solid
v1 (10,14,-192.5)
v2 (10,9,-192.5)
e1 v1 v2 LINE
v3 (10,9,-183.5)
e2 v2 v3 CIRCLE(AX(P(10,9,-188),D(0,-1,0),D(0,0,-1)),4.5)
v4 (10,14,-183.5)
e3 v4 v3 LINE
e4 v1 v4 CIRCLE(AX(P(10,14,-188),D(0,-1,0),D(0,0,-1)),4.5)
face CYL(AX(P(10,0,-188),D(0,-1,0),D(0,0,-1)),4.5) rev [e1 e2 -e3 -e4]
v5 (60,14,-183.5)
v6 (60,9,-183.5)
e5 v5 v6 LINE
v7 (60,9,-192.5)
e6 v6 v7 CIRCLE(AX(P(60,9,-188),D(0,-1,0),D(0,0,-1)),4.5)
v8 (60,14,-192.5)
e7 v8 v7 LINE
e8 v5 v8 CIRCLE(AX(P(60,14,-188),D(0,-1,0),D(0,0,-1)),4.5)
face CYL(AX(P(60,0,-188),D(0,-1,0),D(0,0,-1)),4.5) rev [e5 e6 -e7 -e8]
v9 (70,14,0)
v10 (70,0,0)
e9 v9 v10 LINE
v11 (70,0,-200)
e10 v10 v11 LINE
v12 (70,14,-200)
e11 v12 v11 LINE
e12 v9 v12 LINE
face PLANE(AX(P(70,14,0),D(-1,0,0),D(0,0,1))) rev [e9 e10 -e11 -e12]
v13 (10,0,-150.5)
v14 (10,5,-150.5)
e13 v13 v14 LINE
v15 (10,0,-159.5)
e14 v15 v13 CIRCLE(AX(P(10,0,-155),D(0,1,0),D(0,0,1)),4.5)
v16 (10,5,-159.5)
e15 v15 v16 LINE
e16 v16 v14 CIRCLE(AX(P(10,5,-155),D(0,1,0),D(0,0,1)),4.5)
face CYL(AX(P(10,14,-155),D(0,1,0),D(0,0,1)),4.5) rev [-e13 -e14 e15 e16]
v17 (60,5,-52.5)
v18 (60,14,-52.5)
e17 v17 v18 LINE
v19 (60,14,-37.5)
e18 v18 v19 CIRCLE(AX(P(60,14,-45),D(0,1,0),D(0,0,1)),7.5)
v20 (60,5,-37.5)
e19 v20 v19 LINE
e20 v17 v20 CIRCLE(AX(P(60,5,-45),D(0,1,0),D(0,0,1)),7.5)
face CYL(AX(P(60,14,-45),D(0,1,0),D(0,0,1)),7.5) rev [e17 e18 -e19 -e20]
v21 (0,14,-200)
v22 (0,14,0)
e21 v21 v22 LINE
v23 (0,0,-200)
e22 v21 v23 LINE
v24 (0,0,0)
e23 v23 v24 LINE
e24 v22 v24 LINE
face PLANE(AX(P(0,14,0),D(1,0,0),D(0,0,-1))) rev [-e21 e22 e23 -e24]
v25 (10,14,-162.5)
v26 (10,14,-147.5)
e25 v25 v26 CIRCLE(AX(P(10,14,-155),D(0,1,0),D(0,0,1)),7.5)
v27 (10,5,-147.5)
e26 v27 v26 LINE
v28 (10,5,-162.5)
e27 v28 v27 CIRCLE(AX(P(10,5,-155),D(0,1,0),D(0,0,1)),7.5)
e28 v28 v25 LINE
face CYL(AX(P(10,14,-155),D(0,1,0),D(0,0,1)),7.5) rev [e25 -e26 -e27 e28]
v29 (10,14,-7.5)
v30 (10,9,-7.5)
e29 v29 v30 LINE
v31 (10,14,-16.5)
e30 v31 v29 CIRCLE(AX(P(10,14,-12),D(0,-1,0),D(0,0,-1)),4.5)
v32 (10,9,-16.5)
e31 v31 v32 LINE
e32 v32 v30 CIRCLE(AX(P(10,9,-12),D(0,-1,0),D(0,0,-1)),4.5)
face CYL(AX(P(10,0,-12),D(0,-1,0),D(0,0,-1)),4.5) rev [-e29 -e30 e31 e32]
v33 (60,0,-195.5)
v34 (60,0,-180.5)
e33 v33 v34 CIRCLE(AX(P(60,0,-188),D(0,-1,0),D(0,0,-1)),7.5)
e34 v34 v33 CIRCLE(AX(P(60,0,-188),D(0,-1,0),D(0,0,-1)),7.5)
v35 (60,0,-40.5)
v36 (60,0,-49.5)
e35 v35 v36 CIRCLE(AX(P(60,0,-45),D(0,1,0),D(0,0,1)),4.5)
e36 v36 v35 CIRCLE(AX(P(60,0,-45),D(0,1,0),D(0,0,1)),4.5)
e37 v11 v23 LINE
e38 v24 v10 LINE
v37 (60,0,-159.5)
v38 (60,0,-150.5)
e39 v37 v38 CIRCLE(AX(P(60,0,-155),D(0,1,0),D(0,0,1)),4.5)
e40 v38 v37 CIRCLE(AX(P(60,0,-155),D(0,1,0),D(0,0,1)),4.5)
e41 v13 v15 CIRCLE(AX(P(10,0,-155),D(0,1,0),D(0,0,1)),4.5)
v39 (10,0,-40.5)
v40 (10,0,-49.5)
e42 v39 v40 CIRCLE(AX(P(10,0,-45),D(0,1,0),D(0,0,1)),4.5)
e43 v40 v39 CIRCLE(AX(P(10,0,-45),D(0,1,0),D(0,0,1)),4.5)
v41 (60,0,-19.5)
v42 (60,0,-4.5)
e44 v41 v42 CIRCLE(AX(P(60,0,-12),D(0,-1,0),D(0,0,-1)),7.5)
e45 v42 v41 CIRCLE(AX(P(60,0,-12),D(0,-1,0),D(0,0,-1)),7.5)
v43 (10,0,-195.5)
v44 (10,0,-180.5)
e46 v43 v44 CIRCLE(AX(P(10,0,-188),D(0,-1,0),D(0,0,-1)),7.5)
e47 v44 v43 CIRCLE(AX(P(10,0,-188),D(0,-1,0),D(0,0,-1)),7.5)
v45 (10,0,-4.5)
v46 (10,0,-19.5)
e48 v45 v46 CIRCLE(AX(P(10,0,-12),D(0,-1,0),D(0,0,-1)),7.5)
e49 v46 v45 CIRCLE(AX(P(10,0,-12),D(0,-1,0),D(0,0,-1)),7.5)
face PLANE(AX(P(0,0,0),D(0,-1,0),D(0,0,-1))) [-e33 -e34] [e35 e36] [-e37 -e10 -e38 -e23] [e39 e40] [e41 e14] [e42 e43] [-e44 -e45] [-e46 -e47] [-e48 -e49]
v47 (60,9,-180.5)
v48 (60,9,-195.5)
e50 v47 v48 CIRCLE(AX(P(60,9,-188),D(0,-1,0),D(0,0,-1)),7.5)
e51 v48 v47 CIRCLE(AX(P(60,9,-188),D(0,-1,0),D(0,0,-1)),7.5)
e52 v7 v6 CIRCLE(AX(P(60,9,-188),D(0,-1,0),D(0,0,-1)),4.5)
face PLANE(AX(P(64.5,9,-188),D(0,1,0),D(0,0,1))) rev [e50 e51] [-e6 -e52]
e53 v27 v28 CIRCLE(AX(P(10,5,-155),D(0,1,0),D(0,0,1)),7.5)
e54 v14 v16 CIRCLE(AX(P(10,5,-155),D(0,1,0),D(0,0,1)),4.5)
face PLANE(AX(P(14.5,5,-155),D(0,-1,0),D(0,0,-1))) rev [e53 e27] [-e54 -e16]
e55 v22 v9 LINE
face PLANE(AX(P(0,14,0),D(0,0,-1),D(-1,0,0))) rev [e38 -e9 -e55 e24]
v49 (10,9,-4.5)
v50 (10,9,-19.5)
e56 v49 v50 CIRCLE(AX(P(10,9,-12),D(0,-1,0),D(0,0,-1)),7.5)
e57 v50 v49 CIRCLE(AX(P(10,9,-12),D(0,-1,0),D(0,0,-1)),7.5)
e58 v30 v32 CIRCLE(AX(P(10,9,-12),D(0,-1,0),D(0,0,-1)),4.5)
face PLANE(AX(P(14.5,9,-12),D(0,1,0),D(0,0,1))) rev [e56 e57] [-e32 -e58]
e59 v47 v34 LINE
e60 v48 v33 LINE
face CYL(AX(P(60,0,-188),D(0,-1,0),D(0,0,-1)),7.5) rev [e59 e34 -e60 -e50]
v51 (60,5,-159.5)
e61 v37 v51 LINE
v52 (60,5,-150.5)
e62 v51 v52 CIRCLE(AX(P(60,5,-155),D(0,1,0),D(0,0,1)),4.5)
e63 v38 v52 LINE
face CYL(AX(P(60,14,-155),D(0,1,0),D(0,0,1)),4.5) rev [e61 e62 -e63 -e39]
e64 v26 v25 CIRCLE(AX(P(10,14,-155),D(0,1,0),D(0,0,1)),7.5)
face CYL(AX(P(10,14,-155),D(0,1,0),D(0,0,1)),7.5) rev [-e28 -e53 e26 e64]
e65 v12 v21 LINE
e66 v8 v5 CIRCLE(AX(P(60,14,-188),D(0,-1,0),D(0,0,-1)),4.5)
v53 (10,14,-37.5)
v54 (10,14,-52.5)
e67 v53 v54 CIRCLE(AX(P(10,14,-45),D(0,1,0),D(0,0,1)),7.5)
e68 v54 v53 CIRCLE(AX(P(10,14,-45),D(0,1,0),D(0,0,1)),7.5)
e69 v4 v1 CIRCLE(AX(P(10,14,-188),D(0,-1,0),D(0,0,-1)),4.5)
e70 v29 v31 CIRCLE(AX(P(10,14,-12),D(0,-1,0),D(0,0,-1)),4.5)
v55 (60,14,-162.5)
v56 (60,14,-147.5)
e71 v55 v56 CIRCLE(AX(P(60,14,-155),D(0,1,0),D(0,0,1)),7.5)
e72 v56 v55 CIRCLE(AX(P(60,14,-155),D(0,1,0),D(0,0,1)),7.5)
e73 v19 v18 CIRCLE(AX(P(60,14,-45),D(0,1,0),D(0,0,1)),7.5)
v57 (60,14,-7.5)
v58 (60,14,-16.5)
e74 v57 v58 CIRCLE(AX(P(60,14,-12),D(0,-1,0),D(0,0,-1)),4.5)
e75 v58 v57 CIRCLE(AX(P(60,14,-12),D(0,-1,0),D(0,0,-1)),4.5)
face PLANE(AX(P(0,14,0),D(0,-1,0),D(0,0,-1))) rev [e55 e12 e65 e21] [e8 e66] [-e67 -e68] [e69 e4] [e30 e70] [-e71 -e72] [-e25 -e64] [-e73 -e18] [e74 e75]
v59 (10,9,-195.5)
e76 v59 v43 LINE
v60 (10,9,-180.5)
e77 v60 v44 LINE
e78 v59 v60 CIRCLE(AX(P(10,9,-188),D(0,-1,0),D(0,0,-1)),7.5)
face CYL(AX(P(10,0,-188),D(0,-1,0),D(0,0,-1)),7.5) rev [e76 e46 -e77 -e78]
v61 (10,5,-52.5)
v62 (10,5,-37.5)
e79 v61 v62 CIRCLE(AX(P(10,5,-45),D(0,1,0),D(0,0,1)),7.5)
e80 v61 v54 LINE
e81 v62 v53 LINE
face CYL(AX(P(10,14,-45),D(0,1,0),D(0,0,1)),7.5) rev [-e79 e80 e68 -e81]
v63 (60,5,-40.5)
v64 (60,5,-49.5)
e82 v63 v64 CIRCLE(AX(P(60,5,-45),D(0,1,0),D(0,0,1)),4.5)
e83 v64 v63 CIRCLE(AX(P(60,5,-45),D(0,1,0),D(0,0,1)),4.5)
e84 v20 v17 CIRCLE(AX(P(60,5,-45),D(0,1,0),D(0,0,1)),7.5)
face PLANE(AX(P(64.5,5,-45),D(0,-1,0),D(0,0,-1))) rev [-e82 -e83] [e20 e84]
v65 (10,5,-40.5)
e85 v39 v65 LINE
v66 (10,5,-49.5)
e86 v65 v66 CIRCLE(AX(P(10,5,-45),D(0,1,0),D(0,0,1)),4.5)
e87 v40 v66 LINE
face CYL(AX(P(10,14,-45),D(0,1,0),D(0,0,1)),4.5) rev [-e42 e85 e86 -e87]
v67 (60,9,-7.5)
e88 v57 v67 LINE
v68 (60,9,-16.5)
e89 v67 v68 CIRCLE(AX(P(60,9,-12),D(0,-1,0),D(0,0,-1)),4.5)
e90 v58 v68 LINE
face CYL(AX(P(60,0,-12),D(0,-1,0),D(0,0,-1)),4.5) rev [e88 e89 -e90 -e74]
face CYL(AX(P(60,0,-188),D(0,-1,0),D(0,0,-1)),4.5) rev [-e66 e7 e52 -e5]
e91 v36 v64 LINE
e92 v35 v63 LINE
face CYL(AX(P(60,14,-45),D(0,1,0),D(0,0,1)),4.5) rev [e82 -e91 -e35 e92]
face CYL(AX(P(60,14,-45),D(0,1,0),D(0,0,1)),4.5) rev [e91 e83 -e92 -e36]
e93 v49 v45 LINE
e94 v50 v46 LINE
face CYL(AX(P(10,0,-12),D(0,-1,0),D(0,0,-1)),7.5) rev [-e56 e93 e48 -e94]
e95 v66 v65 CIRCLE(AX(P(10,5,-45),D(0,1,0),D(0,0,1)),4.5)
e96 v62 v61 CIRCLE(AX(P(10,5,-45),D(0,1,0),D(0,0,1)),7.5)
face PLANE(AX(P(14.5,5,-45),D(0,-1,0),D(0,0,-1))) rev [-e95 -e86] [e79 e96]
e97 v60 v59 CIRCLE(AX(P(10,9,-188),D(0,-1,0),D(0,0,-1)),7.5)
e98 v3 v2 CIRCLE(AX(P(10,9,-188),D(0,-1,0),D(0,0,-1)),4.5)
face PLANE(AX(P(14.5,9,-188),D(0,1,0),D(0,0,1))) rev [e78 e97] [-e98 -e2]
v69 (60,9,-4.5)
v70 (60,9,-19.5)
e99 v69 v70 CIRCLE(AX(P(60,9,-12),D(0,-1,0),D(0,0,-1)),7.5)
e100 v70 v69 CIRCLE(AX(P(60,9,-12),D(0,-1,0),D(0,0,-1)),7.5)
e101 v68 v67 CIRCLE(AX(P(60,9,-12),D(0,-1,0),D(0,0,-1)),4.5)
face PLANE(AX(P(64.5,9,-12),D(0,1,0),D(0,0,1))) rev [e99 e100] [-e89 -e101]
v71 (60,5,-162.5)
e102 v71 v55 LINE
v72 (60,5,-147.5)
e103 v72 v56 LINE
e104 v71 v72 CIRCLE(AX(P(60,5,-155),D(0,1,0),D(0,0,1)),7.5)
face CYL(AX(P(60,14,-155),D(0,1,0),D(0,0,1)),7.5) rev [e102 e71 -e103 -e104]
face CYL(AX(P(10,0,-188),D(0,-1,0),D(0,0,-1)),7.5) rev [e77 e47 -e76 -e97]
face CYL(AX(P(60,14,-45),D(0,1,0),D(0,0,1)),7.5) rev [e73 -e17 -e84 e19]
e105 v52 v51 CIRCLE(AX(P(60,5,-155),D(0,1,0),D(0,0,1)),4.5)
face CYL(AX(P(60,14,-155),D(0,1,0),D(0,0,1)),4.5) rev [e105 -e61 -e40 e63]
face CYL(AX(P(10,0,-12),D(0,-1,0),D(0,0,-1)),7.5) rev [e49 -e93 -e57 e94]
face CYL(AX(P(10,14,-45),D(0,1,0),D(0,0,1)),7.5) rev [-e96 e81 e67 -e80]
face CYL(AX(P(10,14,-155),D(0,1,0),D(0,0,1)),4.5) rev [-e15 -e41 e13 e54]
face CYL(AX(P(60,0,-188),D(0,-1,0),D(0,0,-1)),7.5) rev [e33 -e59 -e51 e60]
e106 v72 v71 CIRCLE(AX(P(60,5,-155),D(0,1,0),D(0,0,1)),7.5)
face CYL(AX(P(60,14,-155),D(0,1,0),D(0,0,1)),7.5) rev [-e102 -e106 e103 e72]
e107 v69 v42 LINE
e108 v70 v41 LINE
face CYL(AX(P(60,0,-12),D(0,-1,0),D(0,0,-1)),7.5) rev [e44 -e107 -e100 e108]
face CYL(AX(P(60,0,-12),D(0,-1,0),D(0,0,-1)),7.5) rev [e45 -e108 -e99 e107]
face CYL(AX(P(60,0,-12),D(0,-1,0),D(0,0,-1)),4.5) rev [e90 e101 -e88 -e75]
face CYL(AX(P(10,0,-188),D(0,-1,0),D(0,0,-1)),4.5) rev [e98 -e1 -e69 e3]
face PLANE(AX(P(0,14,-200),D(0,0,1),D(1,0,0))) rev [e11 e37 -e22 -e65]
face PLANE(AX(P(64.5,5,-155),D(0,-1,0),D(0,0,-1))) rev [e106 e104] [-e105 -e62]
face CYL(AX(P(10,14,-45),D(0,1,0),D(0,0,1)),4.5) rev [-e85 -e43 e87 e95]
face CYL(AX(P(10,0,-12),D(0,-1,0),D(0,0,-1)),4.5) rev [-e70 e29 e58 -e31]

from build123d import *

# Parameters (mm, degrees)
SKETCH1_W                                          = 70
SKETCH1_H                                          = 200
BOSS_EXTRUDE1_DEPTH                                = 14
HOLE_SIZE_BASED_ON_SOCKET_HEAD_CAP_SCR_D           = 9
HOLE_SIZE_BASED_ON_SOCKET_HEAD_CAP_SCR_CBORE_D     = 15
HOLE_SIZE_BASED_ON_SOCKET_HEAD_CAP_SCR_CBORE_DEPTH = 9
HOLE_SIZE_BASED_ON_SOCKET_HEAD_CAP_2_D             = 9
HOLE_SIZE_BASED_ON_SOCKET_HEAD_CAP_2_CBORE_D       = 15
HOLE_SIZE_BASED_ON_SOCKET_HEAD_CAP_2_CBORE_DEPTH   = 9


with BuildPart() as part:
    # Sketch1 → Boss-Extrude1 (new body)
    with BuildSketch(Plane(origin=(0, 0, 0), x_dir=(1, 0, 0), z_dir=(0, 1, 0))):
        with Locations((35, 100)):
            Rectangle(SKETCH1_W, SKETCH1_H)
    extrude(amount=BOSS_EXTRUDE1_DEPTH)

    # Hole size _based on_ socket head cap scr (through all)
    with Locations(Plane(origin=(0, 14, 0), x_dir=(1, 0, 0), z_dir=(0, 1, 0))):
        with Locations((10, 155), (60, 155), (60, 45), (10, 45)):
            CounterBoreHole(HOLE_SIZE_BASED_ON_SOCKET_HEAD_CAP_SCR_D / 2, HOLE_SIZE_BASED_ON_SOCKET_HEAD_CAP_SCR_CBORE_D / 2, HOLE_SIZE_BASED_ON_SOCKET_HEAD_CAP_SCR_CBORE_DEPTH)

    # Hole size _based on_ socket head cap 2 (through all)
    with Locations(Plane(origin=(0, 0, 0), x_dir=(-1, 0, 0), z_dir=(0, -1, 0))):
        with Locations((-60, 188), (-10, 188), (-10, 12), (-60, 12)):
            CounterBoreHole(HOLE_SIZE_BASED_ON_SOCKET_HEAD_CAP_2_D / 2, HOLE_SIZE_BASED_ON_SOCKET_HEAD_CAP_2_CBORE_D / 2, HOLE_SIZE_BASED_ON_SOCKET_HEAD_CAP_2_CBORE_DEPTH)


solid = part.part
